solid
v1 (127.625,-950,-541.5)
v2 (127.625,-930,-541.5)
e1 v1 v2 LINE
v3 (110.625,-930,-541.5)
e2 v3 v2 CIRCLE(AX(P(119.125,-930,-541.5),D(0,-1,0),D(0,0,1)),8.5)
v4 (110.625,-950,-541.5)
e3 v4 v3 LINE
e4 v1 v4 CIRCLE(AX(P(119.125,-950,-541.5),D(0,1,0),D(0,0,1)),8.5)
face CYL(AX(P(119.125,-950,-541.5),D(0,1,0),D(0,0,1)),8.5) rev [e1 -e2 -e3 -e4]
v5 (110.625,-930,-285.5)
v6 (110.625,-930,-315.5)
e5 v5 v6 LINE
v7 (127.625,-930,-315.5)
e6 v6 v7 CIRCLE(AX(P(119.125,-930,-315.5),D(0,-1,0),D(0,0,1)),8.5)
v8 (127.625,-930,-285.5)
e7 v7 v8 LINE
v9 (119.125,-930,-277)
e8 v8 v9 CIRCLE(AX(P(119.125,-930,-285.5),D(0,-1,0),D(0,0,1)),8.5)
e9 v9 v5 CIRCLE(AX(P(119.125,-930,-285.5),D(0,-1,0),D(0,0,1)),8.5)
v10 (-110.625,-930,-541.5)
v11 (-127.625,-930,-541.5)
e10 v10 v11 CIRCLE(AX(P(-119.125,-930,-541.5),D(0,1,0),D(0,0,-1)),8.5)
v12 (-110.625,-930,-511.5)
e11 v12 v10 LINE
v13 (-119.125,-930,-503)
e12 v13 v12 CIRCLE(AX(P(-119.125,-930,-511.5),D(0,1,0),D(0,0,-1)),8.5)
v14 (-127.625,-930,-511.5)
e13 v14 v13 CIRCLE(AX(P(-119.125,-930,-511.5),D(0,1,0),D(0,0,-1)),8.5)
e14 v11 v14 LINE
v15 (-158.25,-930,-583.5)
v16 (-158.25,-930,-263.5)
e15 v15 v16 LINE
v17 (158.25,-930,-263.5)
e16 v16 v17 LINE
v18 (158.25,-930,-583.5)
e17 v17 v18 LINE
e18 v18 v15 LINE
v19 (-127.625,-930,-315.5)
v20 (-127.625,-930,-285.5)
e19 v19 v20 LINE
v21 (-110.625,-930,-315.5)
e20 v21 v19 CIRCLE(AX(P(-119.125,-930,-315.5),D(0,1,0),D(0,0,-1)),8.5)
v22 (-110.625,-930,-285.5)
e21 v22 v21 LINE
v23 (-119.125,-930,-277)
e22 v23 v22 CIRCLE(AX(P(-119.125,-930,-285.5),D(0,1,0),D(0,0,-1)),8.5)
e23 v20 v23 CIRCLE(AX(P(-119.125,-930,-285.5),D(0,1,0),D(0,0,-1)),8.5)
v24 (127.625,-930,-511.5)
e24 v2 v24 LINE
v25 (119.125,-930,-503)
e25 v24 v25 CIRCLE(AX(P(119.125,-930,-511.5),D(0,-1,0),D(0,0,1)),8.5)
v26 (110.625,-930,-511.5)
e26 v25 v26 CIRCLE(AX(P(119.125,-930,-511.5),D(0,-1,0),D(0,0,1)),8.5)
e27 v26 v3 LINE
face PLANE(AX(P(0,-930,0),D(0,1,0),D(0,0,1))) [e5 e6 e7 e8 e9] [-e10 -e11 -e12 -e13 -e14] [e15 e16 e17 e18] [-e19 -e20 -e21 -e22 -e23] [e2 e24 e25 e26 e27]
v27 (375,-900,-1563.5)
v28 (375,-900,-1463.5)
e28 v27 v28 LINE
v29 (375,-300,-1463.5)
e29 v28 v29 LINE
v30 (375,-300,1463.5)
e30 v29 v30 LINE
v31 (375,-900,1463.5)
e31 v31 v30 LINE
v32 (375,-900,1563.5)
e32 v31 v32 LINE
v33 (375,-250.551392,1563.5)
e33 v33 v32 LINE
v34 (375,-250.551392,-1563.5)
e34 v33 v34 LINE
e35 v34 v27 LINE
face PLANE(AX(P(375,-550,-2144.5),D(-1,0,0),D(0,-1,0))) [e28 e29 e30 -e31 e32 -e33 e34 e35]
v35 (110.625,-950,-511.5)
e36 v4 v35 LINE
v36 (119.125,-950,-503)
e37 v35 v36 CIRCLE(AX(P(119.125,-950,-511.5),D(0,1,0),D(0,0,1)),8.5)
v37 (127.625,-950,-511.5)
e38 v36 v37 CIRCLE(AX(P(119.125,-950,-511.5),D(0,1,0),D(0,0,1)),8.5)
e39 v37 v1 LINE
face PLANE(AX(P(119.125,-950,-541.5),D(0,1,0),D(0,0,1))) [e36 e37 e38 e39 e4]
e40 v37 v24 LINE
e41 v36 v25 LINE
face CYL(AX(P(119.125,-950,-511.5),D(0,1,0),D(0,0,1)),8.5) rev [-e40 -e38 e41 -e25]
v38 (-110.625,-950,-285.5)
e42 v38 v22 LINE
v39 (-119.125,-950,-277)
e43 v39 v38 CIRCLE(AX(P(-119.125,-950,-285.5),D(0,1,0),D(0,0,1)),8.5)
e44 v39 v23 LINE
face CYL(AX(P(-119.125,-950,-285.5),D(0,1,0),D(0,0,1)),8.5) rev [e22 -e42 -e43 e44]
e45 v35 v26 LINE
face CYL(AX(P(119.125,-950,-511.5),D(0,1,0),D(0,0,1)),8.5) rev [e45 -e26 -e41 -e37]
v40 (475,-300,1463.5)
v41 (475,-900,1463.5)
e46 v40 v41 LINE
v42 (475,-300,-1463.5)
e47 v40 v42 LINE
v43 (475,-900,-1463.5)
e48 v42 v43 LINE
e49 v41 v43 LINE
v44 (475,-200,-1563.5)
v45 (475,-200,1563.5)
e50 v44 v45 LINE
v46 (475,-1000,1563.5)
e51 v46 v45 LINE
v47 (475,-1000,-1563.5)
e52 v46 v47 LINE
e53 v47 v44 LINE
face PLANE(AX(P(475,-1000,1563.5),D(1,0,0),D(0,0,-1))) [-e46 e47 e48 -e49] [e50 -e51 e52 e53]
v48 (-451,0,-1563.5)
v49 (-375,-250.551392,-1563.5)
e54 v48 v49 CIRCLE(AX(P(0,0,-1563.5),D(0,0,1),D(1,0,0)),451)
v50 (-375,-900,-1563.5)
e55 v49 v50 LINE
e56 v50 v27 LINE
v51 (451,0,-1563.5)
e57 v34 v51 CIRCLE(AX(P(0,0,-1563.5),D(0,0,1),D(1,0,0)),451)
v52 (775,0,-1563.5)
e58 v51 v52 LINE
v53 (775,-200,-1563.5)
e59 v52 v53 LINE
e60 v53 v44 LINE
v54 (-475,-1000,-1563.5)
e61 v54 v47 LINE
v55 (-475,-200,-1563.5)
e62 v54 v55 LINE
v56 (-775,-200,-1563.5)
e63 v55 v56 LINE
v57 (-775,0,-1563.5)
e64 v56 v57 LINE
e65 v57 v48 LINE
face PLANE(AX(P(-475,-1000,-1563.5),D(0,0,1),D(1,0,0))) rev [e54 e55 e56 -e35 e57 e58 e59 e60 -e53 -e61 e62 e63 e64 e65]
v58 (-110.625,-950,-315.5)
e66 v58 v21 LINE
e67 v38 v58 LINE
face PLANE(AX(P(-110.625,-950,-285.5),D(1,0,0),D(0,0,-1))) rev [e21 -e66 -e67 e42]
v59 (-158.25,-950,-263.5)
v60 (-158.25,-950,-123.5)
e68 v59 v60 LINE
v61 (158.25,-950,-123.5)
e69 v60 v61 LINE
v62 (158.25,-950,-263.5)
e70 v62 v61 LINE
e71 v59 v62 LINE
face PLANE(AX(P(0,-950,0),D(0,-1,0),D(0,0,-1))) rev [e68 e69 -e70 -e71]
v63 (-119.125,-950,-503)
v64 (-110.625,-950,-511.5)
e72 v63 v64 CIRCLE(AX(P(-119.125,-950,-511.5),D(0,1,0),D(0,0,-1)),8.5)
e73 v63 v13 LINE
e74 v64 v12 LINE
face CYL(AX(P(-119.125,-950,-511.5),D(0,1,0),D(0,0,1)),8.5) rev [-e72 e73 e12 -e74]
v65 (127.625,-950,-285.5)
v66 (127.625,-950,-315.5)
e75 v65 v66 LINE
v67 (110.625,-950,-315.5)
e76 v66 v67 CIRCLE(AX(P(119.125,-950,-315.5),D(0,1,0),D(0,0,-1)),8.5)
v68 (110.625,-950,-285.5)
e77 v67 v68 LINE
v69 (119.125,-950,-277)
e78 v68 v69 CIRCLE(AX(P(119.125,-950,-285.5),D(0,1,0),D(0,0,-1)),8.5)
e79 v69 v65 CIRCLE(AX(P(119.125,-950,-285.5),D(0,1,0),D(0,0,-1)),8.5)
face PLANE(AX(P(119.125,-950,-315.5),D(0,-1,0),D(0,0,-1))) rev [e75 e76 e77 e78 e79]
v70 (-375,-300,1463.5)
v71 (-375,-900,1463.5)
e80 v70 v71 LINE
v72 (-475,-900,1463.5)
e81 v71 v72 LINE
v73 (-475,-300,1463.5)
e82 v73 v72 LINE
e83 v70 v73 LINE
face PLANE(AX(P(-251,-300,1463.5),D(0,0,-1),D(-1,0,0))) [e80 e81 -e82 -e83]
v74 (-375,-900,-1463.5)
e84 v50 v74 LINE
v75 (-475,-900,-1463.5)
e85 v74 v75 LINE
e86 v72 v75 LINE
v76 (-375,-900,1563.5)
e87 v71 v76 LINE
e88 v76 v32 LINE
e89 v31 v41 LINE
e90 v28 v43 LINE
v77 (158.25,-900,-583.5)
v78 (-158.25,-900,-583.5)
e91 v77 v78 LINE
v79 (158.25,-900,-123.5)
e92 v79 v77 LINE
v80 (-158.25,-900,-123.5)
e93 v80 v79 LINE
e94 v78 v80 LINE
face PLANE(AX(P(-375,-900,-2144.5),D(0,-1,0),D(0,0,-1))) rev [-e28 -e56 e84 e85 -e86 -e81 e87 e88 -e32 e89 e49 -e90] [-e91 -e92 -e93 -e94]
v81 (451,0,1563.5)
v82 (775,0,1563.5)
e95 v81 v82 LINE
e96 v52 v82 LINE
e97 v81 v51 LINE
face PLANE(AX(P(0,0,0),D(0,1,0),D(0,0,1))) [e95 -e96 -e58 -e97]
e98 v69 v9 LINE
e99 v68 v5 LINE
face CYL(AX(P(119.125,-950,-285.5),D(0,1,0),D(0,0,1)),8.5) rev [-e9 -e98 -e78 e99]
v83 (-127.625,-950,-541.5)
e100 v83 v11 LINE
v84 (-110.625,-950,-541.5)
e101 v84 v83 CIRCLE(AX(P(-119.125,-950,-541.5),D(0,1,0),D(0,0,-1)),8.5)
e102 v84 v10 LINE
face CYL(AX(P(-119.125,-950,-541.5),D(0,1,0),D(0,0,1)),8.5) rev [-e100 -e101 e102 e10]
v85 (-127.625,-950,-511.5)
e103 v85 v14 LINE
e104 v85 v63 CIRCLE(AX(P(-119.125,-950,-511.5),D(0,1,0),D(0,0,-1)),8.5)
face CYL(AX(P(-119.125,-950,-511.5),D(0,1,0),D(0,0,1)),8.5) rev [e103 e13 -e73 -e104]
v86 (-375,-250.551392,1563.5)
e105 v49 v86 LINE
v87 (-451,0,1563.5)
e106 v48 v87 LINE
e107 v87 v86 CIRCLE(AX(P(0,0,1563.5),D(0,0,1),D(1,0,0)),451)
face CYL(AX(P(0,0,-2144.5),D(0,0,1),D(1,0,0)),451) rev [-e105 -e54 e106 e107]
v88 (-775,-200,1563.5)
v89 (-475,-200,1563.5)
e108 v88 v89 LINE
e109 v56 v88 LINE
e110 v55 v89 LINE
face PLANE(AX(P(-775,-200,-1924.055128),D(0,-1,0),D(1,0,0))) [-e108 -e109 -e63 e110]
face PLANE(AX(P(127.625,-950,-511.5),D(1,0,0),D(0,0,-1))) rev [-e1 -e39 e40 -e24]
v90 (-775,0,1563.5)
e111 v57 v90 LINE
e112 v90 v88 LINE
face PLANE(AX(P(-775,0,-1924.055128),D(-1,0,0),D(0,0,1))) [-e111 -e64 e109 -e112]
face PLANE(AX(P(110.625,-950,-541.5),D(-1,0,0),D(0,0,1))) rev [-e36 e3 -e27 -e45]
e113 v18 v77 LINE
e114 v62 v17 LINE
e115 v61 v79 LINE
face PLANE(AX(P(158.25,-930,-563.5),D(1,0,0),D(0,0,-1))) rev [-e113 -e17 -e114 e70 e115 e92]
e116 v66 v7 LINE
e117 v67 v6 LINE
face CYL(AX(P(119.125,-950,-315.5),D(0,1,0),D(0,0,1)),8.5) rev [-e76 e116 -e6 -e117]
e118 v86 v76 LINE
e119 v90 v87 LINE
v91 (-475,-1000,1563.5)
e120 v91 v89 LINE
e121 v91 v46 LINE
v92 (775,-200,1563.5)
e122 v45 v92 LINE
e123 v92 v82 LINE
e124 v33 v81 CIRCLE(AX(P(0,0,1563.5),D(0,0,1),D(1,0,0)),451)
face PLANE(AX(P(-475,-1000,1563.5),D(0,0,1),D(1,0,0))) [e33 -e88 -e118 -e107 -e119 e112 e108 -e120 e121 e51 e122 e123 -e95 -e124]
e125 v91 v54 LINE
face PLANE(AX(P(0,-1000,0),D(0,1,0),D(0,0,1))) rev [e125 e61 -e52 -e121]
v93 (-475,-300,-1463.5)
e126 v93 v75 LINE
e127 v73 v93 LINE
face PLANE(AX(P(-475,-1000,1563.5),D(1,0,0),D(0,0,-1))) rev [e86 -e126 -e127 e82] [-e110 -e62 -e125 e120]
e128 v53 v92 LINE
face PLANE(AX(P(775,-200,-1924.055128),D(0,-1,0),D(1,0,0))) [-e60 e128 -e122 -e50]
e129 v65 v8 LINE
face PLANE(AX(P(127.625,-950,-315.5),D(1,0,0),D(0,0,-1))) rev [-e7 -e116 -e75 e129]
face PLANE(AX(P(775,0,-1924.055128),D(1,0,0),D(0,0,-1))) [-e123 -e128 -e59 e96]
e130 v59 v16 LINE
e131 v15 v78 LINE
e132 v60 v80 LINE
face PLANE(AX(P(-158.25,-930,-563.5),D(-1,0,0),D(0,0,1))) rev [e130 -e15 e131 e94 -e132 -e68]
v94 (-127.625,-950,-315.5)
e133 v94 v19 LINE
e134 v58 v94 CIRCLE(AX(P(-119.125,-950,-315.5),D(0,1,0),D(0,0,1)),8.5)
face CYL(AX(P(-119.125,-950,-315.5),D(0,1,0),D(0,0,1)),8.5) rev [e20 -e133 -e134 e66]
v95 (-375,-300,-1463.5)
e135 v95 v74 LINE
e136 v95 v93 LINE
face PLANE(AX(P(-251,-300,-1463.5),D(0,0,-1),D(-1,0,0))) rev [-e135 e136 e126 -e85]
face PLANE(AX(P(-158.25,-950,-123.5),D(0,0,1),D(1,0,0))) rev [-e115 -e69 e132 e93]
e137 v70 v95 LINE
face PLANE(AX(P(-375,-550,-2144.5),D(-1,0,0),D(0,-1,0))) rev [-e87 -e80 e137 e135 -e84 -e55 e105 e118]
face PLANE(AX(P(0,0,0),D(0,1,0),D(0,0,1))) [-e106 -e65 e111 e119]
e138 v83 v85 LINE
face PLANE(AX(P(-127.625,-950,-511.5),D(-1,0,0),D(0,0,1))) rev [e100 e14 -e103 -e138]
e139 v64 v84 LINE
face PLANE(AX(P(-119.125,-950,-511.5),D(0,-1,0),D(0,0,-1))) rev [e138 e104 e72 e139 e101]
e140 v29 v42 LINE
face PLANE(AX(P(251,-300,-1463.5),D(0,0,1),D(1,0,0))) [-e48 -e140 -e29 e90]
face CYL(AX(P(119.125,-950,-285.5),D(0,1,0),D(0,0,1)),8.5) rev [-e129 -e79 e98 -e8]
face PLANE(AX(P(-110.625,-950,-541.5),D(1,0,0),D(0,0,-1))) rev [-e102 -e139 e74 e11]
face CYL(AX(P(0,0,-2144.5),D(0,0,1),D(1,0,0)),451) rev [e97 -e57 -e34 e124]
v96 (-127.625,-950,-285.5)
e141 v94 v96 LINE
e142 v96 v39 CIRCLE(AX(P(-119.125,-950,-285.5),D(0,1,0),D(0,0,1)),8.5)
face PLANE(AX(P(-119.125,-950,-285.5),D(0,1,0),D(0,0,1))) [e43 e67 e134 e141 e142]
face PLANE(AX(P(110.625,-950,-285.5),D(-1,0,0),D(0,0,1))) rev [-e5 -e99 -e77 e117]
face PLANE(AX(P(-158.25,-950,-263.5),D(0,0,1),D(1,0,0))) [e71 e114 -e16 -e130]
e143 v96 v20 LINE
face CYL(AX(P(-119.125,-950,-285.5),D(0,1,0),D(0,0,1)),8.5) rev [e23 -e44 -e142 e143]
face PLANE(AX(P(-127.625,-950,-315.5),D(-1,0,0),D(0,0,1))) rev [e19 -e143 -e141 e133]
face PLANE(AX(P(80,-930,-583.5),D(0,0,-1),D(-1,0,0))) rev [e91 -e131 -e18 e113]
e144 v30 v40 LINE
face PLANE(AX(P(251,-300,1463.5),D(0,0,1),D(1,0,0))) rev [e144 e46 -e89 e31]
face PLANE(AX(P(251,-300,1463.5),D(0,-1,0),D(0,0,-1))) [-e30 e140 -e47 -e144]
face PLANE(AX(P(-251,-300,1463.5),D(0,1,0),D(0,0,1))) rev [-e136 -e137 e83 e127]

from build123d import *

# Parameters (mm, degrees)
SKETCH_2_W          = 950
SKETCH_2_H          = 3127
EXTRUDE_1_DEPTH     = 1000
SKETCH_4_R          = 451
CUT_EXTRUDE_1_DEPTH = 3708
SKETCH_6_W          = 300
SKETCH_6_H          = 200
EXTRUDE_2_DEPTH     = 3127
SKETCH_9_W          = 750
SKETCH_9_H          = 350
CUT_EXTRUDE_2_DEPTH = 3708
SKETCH_10_W         = 750
SKETCH_10_H         = 3127
CUT_EXTRUDE_3_DEPTH = 3708
CUT_EXTRUDE_4_DEPTH = 50
SKETCH_12_W         = 78.25
SKETCH_12_H         = 300
CUT_EXTRUDE_5_DEPTH = 30
SKETCH_13_W         = 78.25
SKETCH_13_H         = 20
CUT_EXTRUDE_6_DEPTH = 30
SKETCH_14_W         = 160
SKETCH_14_H         = 320
CUT_EXTRUDE_7_DEPTH = 30
SKETCH_15_W         = 2927
SKETCH_15_H         = 600
CUT_EXTRUDE_8_DEPTH = 224
SKETCH_16_W         = 316.5
SKETCH_16_H         = 140
CUT_EXTRUDE_9_DEPTH = 50


with BuildPart() as part:
    # 草图2 → 凸台-拉伸1 (new body)
    with BuildSketch(Plane(origin=(0, 0, 0), x_dir=(1, 0, 0), z_dir=(0, 1, 0))):
        Rectangle(SKETCH_2_W, SKETCH_2_H)
    extrude(amount=-EXTRUDE_1_DEPTH)

    # 草图4 → 切除-拉伸1 (cut)
    with BuildSketch(Plane.XY.offset(1563.5)):
        Circle(SKETCH_4_R)
    extrude(amount=-CUT_EXTRUDE_1_DEPTH, mode=Mode.SUBTRACT)

    # 草图6 → 凸台-拉伸2 (add)
    with BuildSketch(Plane.XY.offset(1563.5)):
        with Locations((-625, -100)):
            Rectangle(SKETCH_6_W, SKETCH_6_H)
        with Locations((625, -100)):
            Rectangle(SKETCH_6_W, SKETCH_6_H)
    extrude(amount=-EXTRUDE_2_DEPTH)

    # 草图9 → 切除-拉伸2 (cut)
    with BuildSketch(Plane.XY.offset(1563.5)):
        with Locations((0, -725)):
            Rectangle(SKETCH_9_W, SKETCH_9_H)
    extrude(amount=-CUT_EXTRUDE_2_DEPTH, mode=Mode.SUBTRACT)

    # 草图10 → 切除-拉伸3 (cut)
    with BuildSketch(Plane(origin=(0, -900, 0), x_dir=(1, 0, 0), z_dir=(0, 1, 0))):
        Rectangle(SKETCH_10_W, SKETCH_10_H)
    extrude(amount=CUT_EXTRUDE_3_DEPTH, mode=Mode.SUBTRACT)

    # 草图11 → 切除-拉伸4 (cut)
    with BuildSketch(Plane(origin=(0, -900, 0), x_dir=(1, 0, 0), z_dir=(0, 1, 0))):
        with BuildLine():
            Line((110.625, 541.5), (110.625, 511.5))
            ThreePointArc((110.625, 511.5), (119.125, 503), (127.625, 511.5))
            Line((127.625, 511.5), (127.625, 541.5))
            ThreePointArc((127.625, 541.5), (119.125, 550), (110.625, 541.5))
        make_face()
        with BuildLine():
            Line((127.625, 315.5), (127.625, 285.5))
            ThreePointArc((127.625, 285.5), (119.125, 277), (110.625, 285.5))
            Line((110.625, 285.5), (110.625, 315.5))
            ThreePointArc((110.625, 315.5), (119.125, 324), (127.625, 315.5))
        make_face()
        with BuildLine():
            Line((-110.625, 285.5), (-110.625, 315.5))
            ThreePointArc((-110.625, 315.5), (-119.125, 324), (-127.625, 315.5))
            Line((-127.625, 315.5), (-127.625, 285.5))
            ThreePointArc((-127.625, 285.5), (-119.125, 277), (-110.625, 285.5))
        make_face()
        with BuildLine():
            Line((-127.625, 511.5), (-127.625, 541.5))
            ThreePointArc((-127.625, 541.5), (-119.125, 550), (-110.625, 541.5))
            Line((-110.625, 541.5), (-110.625, 511.5))
            ThreePointArc((-110.625, 511.5), (-119.125, 503), (-127.625, 511.5))
        make_face()
    extrude(amount=-CUT_EXTRUDE_4_DEPTH, mode=Mode.SUBTRACT)

    # 草图12 → 切除-拉伸5 (cut)
    with BuildSketch(Plane(origin=(0, -900, 0), x_dir=(1, 0, 0), z_dir=(0, 1, 0))):
        with Locations((119.125, 413.5)):
            Rectangle(SKETCH_12_W, SKETCH_12_H)
        with Locations((-119.125, 413.5)):
            Rectangle(SKETCH_12_W, SKETCH_12_H)
    extrude(amount=-CUT_EXTRUDE_5_DEPTH, mode=Mode.SUBTRACT)

    # 草图13 → 切除-拉伸6 (cut)
    with BuildSketch(Plane(origin=(0, -900, 0), x_dir=(1, 0, 0), z_dir=(0, 1, 0))):
        with Locations((119.125, 573.5)):
            Rectangle(SKETCH_13_W, SKETCH_13_H)
        with Locations((-119.125, 573.5)):
            Rectangle(SKETCH_13_W, SKETCH_13_H)
    extrude(amount=-CUT_EXTRUDE_6_DEPTH, mode=Mode.SUBTRACT)

    # 草图14 → 切除-拉伸7 (cut)
    with BuildSketch(Plane(origin=(0, -900, 0), x_dir=(1, 0, 0), z_dir=(0, 1, 0))):
        with Locations((0, 423.5)):
            Rectangle(SKETCH_14_W, SKETCH_14_H)
    extrude(amount=-CUT_EXTRUDE_7_DEPTH, mode=Mode.SUBTRACT)

    # 草图15 → 切除-拉伸8 (cut)
    with BuildSketch(Plane(origin=(475, 0, 0), x_dir=(0, 0, -1), z_dir=(1, 0, 0))):
        with Locations((0, -600)):
            Rectangle(SKETCH_15_W, SKETCH_15_H)
    cut_extrude_8 = extrude(amount=-CUT_EXTRUDE_8_DEPTH, mode=Mode.SUBTRACT)

    # 镜向1: 切除-拉伸8 across plane
    add(cut_extrude_8.mirror(Plane(origin=(0, 0, 0), x_dir=(0, 0, 1), z_dir=(1, 0, 0))), mode=Mode.SUBTRACT)

    # 草图16 → 切除-拉伸9 (cut)
    with BuildSketch(Plane(origin=(0, -900, 0), x_dir=(1, 0, 0), z_dir=(0, 1, 0))):
        with Locations((0, 193.5)):
            Rectangle(SKETCH_16_W, SKETCH_16_H)
    extrude(amount=-CUT_EXTRUDE_9_DEPTH, mode=Mode.SUBTRACT)


solid = part.part
